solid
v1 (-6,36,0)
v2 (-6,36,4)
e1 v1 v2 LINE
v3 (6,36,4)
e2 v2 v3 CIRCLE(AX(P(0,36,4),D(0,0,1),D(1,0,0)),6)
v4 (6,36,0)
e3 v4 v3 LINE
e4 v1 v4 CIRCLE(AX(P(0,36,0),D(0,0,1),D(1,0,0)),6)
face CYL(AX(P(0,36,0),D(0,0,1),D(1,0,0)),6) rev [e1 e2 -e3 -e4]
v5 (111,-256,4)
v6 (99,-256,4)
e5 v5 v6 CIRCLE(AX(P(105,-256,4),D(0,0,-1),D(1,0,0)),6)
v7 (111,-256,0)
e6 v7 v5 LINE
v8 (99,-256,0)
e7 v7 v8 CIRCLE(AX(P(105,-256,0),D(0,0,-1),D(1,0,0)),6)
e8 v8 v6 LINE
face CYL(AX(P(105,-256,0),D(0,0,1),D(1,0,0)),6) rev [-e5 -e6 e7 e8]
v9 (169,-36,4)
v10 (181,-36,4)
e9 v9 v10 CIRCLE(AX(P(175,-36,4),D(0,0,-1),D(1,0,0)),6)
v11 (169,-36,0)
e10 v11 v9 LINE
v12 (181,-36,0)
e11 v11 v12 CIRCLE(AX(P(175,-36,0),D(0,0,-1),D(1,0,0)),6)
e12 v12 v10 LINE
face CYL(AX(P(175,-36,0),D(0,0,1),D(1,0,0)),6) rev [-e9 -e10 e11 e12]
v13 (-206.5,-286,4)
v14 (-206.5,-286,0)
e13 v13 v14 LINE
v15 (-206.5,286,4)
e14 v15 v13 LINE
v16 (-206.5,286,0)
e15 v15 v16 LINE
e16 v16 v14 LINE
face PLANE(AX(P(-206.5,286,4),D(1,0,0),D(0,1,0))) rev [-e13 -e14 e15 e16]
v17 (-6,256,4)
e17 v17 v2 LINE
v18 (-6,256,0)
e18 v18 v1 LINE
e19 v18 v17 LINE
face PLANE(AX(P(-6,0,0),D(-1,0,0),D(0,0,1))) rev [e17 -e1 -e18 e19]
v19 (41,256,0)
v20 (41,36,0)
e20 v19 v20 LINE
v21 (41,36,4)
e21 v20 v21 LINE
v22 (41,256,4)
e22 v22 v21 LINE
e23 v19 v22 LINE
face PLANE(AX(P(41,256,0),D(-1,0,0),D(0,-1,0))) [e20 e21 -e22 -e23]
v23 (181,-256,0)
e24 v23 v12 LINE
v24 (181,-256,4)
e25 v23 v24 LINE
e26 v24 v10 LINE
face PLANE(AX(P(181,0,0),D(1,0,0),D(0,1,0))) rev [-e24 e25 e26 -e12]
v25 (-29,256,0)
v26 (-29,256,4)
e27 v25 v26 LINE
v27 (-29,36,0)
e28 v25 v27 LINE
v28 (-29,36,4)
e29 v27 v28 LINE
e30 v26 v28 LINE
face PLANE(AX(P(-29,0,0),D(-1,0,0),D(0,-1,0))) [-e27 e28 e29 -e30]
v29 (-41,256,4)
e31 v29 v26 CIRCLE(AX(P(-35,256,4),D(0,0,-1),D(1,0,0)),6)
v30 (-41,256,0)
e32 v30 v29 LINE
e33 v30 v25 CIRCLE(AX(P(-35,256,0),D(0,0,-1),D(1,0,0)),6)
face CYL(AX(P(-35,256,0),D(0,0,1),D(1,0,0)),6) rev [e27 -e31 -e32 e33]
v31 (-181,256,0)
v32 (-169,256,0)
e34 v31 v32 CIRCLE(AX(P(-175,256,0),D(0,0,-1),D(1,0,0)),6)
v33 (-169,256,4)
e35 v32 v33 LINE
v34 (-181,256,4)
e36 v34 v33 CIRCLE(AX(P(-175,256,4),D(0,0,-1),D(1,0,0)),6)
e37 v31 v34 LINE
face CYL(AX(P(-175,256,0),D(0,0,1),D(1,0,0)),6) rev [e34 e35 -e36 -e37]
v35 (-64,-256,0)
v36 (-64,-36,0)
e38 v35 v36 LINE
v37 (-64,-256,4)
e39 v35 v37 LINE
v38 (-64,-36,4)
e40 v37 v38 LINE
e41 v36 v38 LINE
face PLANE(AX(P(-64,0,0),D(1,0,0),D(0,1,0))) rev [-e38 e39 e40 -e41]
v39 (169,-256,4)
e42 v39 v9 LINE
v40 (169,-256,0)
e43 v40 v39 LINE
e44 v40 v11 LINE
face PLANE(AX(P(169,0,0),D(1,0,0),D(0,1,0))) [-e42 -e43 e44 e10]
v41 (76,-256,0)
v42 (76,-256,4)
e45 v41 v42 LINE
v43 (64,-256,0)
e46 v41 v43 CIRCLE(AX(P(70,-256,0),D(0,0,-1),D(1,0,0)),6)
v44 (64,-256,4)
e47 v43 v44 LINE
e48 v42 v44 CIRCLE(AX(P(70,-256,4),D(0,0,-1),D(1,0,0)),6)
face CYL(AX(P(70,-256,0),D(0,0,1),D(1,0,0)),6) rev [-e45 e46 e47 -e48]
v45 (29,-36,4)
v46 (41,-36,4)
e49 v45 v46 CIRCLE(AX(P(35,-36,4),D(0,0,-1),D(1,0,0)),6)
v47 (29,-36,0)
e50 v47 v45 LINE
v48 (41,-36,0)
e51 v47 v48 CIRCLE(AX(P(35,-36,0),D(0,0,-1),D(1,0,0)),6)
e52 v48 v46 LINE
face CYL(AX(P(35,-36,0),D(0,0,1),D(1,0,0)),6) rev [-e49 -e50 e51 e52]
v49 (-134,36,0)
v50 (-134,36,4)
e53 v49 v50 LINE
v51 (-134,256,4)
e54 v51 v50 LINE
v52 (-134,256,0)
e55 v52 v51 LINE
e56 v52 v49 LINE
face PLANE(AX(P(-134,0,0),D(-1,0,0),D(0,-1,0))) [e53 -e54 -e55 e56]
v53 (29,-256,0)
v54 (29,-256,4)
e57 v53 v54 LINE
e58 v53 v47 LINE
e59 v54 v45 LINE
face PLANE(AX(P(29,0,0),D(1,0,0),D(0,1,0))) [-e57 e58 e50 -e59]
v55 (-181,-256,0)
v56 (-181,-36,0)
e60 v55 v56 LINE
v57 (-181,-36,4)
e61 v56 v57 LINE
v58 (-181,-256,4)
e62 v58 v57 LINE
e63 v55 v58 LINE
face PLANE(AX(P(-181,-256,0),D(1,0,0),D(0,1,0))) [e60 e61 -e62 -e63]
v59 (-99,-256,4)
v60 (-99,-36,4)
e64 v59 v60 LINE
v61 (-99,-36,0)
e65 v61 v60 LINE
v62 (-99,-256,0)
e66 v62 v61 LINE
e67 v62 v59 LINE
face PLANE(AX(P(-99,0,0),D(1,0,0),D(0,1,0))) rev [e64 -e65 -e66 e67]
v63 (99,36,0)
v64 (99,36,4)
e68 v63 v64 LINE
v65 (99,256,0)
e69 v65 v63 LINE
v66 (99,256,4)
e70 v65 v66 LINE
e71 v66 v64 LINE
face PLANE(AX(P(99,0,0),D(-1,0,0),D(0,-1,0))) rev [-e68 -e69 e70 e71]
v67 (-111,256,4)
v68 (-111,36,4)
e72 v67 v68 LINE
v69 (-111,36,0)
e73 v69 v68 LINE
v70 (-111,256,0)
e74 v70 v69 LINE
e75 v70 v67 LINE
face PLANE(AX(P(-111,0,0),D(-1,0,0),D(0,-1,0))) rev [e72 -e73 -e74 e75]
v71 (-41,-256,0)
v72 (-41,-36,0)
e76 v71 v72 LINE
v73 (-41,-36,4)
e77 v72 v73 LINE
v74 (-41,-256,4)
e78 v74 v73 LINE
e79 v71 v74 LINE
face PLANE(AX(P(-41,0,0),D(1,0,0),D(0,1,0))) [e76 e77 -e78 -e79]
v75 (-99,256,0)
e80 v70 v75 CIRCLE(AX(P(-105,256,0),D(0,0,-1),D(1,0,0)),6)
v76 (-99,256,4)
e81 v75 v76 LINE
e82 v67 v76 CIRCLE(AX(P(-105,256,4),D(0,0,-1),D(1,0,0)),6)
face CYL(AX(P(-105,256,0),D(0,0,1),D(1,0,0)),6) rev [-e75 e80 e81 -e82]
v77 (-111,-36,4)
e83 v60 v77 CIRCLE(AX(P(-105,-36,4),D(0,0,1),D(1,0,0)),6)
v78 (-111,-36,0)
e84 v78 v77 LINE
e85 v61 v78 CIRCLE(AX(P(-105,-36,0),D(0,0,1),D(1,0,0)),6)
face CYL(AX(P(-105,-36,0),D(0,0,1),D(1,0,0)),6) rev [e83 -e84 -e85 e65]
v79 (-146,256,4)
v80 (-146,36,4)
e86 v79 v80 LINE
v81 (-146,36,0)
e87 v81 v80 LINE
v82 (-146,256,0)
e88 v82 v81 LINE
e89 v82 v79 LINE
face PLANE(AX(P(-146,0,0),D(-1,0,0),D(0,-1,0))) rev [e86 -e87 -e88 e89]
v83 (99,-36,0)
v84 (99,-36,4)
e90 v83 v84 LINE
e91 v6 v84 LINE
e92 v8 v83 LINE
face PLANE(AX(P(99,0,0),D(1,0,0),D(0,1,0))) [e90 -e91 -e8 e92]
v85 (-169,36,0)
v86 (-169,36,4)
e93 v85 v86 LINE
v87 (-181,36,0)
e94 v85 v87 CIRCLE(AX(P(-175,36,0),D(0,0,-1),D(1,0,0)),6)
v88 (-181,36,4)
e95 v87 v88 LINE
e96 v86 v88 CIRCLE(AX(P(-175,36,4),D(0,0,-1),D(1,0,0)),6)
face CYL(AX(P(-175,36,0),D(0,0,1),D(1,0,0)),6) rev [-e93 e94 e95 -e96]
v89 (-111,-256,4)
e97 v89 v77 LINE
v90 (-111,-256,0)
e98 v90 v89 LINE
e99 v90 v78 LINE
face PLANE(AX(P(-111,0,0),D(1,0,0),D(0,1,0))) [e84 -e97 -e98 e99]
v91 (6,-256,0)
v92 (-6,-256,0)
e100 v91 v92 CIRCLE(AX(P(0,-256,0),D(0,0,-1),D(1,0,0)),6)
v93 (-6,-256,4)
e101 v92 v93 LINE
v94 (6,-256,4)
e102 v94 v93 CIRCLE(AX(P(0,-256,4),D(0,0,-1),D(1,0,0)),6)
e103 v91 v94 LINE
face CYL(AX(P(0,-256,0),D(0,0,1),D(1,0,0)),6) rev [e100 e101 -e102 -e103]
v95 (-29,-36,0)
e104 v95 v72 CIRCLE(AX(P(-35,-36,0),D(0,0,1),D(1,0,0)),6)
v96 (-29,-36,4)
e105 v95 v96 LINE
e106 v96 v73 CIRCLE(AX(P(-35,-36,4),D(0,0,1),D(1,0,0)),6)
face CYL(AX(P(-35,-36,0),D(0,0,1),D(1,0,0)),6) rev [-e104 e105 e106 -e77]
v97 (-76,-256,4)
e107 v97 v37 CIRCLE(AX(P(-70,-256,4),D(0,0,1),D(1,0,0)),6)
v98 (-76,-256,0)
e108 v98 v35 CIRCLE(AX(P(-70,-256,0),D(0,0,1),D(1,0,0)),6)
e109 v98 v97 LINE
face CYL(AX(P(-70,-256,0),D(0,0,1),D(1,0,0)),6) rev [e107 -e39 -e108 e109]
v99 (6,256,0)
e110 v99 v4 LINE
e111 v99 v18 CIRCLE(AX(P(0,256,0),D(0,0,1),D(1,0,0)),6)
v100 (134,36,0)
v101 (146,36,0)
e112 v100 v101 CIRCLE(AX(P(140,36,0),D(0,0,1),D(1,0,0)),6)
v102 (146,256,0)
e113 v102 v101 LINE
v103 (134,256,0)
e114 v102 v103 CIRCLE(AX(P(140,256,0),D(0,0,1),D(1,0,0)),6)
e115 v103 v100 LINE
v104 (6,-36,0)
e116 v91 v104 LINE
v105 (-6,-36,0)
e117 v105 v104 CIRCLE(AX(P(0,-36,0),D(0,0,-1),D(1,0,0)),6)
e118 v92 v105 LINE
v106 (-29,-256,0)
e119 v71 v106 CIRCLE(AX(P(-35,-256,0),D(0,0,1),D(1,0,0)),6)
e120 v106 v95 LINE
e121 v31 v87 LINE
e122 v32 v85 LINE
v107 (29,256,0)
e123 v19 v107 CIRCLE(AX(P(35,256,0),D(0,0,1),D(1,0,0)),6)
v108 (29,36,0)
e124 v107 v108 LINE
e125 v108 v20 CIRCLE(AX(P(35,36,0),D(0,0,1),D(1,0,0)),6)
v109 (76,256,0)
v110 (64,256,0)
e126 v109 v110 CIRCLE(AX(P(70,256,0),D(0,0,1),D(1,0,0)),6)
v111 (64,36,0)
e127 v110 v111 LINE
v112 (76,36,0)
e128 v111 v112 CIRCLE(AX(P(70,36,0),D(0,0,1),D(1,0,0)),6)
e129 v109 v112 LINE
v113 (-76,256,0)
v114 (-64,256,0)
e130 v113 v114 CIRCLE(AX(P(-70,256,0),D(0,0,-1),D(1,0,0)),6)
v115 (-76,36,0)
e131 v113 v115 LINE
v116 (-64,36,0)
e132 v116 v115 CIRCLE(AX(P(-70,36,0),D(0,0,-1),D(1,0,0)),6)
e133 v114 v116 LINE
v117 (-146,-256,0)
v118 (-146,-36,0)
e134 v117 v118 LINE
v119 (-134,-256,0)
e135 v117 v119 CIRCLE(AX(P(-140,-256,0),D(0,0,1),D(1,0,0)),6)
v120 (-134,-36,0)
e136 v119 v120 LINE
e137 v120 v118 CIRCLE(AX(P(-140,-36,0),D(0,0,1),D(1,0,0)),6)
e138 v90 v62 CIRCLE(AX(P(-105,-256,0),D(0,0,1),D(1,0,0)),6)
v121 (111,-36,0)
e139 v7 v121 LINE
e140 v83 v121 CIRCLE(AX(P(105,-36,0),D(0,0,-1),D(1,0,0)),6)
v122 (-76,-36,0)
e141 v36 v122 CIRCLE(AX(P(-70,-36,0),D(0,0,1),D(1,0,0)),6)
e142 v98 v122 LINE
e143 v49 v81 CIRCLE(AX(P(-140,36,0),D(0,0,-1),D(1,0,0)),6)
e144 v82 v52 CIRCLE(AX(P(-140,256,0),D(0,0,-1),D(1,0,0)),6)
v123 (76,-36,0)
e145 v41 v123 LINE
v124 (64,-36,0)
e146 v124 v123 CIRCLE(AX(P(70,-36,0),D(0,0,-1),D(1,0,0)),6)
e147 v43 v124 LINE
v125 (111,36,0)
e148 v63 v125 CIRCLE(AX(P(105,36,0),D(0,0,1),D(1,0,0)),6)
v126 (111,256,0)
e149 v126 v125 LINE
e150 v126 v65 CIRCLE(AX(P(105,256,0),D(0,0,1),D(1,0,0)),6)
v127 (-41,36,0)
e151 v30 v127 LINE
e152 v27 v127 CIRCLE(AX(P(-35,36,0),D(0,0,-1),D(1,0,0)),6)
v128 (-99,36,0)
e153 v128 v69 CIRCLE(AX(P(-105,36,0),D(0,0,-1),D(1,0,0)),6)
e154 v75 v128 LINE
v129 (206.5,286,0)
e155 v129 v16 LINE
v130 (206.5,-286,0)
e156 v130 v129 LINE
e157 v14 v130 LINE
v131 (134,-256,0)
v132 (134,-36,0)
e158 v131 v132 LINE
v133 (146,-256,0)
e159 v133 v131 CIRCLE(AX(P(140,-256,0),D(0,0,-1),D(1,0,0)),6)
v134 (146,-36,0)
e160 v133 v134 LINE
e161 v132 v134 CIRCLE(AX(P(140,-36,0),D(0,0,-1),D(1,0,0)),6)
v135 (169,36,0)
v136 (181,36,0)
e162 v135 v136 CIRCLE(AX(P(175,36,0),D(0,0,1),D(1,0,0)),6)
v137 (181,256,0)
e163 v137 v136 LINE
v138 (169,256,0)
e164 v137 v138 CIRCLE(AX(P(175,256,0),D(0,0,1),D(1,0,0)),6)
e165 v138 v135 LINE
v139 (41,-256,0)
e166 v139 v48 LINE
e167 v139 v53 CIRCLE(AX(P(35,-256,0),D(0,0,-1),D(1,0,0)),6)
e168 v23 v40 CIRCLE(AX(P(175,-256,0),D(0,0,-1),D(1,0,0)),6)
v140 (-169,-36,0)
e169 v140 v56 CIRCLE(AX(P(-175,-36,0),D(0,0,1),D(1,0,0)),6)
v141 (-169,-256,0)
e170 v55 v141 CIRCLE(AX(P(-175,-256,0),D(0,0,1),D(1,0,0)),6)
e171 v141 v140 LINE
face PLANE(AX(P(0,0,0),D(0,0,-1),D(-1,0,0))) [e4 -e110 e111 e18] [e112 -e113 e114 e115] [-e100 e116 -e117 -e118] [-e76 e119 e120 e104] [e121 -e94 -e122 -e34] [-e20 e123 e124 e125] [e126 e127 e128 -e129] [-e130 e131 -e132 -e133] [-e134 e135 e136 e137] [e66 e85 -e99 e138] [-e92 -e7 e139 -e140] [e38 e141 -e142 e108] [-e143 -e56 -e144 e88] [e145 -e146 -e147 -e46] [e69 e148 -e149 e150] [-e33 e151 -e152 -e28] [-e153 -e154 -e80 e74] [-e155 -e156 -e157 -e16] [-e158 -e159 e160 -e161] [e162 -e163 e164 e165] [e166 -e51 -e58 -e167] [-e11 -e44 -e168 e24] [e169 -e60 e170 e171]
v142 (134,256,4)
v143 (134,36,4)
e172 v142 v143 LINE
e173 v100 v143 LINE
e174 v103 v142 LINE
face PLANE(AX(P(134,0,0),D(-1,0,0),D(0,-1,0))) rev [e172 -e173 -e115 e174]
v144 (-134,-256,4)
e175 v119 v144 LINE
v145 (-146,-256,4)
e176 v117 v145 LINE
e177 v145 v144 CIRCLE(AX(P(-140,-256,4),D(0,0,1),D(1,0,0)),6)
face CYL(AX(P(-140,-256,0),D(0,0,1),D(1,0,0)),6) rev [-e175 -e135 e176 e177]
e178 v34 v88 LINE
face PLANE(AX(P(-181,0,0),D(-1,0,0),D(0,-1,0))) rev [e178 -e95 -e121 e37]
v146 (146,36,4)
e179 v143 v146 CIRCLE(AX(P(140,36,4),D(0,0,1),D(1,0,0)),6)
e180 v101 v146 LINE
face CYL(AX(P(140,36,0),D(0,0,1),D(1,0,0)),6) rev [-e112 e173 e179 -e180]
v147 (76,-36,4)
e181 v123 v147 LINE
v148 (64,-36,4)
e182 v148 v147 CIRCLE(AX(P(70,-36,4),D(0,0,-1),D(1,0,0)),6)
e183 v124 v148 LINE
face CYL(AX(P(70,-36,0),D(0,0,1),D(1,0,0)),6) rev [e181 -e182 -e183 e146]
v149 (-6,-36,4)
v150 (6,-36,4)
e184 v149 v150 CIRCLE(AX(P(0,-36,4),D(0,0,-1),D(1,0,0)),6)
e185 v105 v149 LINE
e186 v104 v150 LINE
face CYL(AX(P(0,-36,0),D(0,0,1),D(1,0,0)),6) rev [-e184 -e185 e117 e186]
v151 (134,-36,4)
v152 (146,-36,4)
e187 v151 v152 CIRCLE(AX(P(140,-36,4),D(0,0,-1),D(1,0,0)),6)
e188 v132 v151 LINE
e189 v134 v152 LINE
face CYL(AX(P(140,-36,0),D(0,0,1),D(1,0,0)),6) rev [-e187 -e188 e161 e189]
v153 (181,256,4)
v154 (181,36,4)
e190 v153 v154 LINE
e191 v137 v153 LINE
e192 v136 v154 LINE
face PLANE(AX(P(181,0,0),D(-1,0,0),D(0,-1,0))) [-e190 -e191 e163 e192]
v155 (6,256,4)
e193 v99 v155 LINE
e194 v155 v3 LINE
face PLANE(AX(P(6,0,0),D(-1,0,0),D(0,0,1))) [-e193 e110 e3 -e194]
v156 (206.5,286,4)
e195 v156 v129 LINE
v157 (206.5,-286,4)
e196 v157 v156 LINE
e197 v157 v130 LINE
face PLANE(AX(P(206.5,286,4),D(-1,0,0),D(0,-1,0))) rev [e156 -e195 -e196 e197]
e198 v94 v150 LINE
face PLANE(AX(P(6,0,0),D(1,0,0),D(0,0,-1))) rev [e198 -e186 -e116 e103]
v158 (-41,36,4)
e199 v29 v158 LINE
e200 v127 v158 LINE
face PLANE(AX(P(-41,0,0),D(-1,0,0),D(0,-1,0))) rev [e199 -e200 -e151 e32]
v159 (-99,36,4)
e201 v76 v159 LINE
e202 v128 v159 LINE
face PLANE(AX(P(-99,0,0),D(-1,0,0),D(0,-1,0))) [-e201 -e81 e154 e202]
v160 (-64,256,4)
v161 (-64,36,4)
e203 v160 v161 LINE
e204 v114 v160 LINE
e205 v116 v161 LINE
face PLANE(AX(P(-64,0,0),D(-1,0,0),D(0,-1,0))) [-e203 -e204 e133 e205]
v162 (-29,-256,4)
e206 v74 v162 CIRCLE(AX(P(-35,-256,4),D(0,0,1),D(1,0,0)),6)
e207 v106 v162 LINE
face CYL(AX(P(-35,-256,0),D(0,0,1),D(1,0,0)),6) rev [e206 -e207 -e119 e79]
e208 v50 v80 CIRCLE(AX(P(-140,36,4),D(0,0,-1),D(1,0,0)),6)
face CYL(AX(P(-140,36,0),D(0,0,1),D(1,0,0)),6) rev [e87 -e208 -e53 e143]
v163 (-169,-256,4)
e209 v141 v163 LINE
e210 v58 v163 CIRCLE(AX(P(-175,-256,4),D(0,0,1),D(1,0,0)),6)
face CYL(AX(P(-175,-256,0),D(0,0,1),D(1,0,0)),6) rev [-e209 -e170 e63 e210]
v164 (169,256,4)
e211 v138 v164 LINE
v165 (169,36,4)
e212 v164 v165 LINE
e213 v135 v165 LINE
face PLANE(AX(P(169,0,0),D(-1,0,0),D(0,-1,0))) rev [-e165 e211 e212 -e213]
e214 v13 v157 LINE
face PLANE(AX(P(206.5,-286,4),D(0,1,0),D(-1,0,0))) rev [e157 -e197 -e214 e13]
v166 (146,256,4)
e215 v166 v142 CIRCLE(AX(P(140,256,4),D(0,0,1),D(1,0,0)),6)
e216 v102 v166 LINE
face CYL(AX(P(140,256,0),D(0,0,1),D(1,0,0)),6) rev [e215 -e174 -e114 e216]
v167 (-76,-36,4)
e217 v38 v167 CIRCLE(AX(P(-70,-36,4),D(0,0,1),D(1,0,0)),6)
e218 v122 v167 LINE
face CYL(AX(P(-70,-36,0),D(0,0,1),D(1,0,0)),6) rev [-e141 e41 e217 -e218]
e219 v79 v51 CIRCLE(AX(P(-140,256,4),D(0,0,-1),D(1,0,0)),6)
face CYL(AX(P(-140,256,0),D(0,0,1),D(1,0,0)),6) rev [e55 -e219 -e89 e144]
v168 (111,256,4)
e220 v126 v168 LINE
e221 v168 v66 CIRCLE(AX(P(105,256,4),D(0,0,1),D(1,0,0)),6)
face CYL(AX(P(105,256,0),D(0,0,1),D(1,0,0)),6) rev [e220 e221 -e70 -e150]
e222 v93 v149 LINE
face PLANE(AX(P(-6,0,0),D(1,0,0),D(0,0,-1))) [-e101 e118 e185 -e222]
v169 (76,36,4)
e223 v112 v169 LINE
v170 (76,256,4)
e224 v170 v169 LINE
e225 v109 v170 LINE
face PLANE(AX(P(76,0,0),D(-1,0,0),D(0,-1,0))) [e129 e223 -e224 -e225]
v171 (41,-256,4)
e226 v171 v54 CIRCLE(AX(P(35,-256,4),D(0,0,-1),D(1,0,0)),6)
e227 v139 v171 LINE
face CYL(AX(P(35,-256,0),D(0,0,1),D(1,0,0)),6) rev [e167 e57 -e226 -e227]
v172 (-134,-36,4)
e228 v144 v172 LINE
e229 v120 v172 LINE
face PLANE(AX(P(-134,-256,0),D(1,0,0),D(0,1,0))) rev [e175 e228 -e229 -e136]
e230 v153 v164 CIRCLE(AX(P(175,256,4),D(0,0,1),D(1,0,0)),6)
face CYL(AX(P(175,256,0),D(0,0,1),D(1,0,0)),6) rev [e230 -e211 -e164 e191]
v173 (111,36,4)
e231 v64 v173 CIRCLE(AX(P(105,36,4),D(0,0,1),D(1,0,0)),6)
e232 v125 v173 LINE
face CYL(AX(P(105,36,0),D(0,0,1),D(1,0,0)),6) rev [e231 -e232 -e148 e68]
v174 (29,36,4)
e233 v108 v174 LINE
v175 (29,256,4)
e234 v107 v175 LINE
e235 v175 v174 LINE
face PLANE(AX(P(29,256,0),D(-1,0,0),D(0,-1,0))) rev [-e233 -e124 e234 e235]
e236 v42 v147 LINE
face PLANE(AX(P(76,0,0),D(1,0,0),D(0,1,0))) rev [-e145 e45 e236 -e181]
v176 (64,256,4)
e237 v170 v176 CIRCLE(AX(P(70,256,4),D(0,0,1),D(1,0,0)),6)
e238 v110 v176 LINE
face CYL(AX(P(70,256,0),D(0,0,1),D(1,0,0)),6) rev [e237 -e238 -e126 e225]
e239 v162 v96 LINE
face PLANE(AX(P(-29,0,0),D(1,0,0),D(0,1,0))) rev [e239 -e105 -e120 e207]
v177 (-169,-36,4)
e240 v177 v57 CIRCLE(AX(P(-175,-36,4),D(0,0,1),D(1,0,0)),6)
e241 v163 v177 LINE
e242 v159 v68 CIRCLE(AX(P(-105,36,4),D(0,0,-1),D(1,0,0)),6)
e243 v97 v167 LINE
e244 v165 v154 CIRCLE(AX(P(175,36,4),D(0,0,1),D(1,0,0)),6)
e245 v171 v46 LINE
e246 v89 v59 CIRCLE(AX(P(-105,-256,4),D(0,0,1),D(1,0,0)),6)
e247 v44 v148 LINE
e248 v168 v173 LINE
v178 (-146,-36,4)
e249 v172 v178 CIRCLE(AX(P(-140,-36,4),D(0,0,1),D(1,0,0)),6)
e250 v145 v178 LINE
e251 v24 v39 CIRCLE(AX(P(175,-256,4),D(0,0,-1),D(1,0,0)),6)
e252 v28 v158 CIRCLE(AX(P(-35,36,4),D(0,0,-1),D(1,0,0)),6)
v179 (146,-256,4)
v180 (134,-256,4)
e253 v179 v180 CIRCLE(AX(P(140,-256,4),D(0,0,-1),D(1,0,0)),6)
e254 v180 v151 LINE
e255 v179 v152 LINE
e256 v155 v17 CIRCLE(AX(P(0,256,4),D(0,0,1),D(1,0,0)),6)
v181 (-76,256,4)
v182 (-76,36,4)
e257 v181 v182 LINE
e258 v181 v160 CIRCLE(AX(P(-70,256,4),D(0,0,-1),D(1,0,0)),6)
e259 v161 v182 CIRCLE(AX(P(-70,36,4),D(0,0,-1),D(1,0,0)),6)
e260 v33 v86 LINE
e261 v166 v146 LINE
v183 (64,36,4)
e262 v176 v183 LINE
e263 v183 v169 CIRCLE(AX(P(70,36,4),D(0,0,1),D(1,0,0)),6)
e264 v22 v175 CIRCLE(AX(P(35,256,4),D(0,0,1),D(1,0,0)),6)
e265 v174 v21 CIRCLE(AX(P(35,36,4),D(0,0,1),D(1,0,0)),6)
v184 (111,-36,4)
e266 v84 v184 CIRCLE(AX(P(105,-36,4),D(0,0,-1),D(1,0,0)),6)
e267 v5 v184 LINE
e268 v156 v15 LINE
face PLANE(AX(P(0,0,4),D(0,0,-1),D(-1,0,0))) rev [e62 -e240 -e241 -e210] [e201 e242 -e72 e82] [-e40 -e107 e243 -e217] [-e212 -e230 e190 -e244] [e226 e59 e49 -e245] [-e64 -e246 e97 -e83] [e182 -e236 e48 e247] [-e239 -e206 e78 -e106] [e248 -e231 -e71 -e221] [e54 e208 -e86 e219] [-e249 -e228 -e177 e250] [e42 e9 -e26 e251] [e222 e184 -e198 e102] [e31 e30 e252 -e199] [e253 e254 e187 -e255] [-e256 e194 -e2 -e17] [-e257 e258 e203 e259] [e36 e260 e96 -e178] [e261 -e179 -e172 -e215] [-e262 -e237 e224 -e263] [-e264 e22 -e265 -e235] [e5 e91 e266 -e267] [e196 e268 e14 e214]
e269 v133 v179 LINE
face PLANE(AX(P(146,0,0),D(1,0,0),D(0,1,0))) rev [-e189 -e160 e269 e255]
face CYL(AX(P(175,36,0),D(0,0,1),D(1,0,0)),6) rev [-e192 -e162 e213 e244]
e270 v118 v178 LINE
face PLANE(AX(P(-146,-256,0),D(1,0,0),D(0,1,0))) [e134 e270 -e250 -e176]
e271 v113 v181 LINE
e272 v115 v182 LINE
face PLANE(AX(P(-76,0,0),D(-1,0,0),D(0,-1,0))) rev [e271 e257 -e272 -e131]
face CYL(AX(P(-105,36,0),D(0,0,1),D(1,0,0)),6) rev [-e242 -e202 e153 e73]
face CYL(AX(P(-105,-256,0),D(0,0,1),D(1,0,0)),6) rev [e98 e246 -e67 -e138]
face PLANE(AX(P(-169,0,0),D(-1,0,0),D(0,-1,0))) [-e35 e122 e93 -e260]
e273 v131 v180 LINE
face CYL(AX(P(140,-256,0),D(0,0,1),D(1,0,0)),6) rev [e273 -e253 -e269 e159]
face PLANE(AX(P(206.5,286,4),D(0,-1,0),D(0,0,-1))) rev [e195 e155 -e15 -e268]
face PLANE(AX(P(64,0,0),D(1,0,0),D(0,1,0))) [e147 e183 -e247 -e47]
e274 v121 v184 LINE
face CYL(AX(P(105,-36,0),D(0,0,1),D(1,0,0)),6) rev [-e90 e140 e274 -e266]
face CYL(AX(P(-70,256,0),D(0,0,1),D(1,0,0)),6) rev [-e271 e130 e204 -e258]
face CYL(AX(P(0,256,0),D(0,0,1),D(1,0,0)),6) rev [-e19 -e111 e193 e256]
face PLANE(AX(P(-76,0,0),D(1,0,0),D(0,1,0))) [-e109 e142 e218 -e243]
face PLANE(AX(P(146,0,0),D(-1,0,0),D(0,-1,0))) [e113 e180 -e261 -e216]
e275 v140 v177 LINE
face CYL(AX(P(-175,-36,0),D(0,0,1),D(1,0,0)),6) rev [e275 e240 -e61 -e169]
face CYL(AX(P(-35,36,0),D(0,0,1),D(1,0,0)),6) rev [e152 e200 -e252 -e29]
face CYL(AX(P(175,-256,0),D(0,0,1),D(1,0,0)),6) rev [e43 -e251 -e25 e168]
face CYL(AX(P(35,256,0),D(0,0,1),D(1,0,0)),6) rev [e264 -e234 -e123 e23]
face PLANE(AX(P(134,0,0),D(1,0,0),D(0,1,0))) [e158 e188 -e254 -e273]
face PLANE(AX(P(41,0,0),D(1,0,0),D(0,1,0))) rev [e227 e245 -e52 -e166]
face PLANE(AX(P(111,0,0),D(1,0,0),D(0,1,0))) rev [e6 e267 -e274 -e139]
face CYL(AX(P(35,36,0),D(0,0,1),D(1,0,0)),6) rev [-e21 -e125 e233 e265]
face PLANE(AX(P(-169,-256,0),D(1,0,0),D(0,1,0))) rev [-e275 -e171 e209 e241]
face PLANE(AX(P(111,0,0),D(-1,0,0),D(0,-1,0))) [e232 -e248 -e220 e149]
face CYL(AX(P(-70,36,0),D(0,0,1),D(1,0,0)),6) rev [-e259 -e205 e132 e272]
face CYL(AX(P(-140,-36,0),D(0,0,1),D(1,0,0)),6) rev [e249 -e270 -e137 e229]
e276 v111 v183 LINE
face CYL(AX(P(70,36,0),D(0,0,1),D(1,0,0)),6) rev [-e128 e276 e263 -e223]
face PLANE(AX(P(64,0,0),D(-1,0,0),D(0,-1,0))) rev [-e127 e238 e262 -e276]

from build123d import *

# Parameters (mm, degrees)
SKETCH1_W           = 413
SKETCH1_H           = 572
BOSS_EXTRUDE1_DEPTH = 4
CUT_EXTRUDE1_DEPTH  = 4


with BuildPart() as part:
    # Sketch1 → Boss-Extrude1 (new body)
    with BuildSketch(Plane.XY):
        Rectangle(SKETCH1_W, SKETCH1_H)
    extrude(amount=BOSS_EXTRUDE1_DEPTH)

    # Sketch2 → Cut-Extrude1 (cut)
    with BuildSketch(Plane.XY.offset(4)):
        with BuildLine():
            Line((-99, -256), (-99, -36))
            ThreePointArc((-99, -36), (-105, -30), (-111, -36))
            Line((-111, -36), (-111, -256))
            ThreePointArc((-111, -256), (-105, -262), (-99, -256))
        make_face()
        with BuildLine():
            Line((-64, -256), (-64, -36))
            ThreePointArc((-64, -36), (-70, -30), (-76, -36))
            Line((-76, -36), (-76, -256))
            ThreePointArc((-76, -256), (-70, -262), (-64, -256))
        make_face()
        with BuildLine():
            Line((-29, -256), (-29, -36))
            ThreePointArc((-29, -36), (-35, -30), (-41, -36))
            Line((-41, -36), (-41, -256))
            ThreePointArc((-41, -256), (-35, -262), (-29, -256))
        make_face()
        with BuildLine():
            ThreePointArc((-6, -36), (0, -30), (6, -36))
            Line((6, -36), (6, -256))
            ThreePointArc((6, -256), (0, -262), (-6, -256))
            Line((-6, -256), (-6, -36))
        make_face()
        with BuildLine():
            ThreePointArc((29, -36), (35, -30), (41, -36))
            Line((41, -36), (41, -256))
            ThreePointArc((41, -256), (35, -262), (29, -256))
            Line((29, -256), (29, -36))
        make_face()
        with BuildLine():
            ThreePointArc((64, -36), (70, -30), (76, -36))
            Line((76, -36), (76, -256))
            ThreePointArc((76, -256), (70, -262), (64, -256))
            Line((64, -256), (64, -36))
        make_face()
        with BuildLine():
            ThreePointArc((169, -36), (175, -30), (181, -36))
            Line((181, -36), (181, -256))
            ThreePointArc((181, -256), (175, -262), (169, -256))
            Line((169, -256), (169, -36))
        make_face()
        with BuildLine():
            ThreePointArc((134, -36), (140, -30), (146, -36))
            Line((146, -36), (146, -256))
            ThreePointArc((146, -256), (140, -262), (134, -256))
            Line((134, -256), (134, -36))
        make_face()
        with BuildLine():
            ThreePointArc((99, -36), (105, -30), (111, -36))
            Line((111, -36), (111, -256))
            ThreePointArc((111, -256), (105, -262), (99, -256))
            Line((99, -256), (99, -36))
        make_face()
        with BuildLine():
            ThreePointArc((-169, 36), (-175, 30), (-181, 36))
            Line((-181, 36), (-181, 256))
            ThreePointArc((-181, 256), (-175, 262), (-169, 256))
            Line((-169, 256), (-169, 36))
        make_face()
        with BuildLine():
            ThreePointArc((-134, 36), (-140, 30), (-146, 36))
            Line((-146, 36), (-146, 256))
            ThreePointArc((-146, 256), (-140, 262), (-134, 256))
            Line((-134, 256), (-134, 36))
        make_face()
        with BuildLine():
            ThreePointArc((-99, 36), (-105, 30), (-111, 36))
            Line((-111, 36), (-111, 256))
            ThreePointArc((-111, 256), (-105, 262), (-99, 256))
            Line((-99, 256), (-99, 36))
        make_face()
        with BuildLine():
            ThreePointArc((-64, 36), (-70, 30), (-76, 36))
            Line((-76, 36), (-76, 256))
            ThreePointArc((-76, 256), (-70, 262), (-64, 256))
            Line((-64, 256), (-64, 36))
        make_face()
        with BuildLine():
            ThreePointArc((-29, 36), (-35, 30), (-41, 36))
            Line((-41, 36), (-41, 256))
            ThreePointArc((-41, 256), (-35, 262), (-29, 256))
            Line((-29, 256), (-29, 36))
        make_face()
        with BuildLine():
            Line((-6, 256), (-6, 36))
            ThreePointArc((-6, 36), (0, 30), (6, 36))
            Line((6, 36), (6, 256))
            ThreePointArc((6, 256), (0, 262), (-6, 256))
        make_face()
        with BuildLine():
            Line((64, 256), (64, 36))
            ThreePointArc((64, 36), (70, 30), (76, 36))
            Line((76, 36), (76, 256))
            ThreePointArc((76, 256), (70, 262), (64, 256))
        make_face()
        with BuildLine():
            Line((99, 256), (99, 36))
            ThreePointArc((99, 36), (105, 30), (111, 36))
            Line((111, 36), (111, 256))
            ThreePointArc((111, 256), (105, 262), (99, 256))
        make_face()
        with BuildLine():
            Line((134, 256), (134, 36))
            ThreePointArc((134, 36), (140, 30), (146, 36))
            Line((146, 36), (146, 256))
            ThreePointArc((146, 256), (140, 262), (134, 256))
        make_face()
        with BuildLine():
            Line((169, 256), (169, 36))
            ThreePointArc((169, 36), (175, 30), (181, 36))
            Line((181, 36), (181, 256))
            ThreePointArc((181, 256), (175, 262), (169, 256))
        make_face()
        with BuildLine():
            Line((-181, -256), (-181, -36))
            ThreePointArc((-181, -36), (-175, -30), (-169, -36))
            Line((-169, -36), (-169, -256))
            ThreePointArc((-169, -256), (-175, -262), (-181, -256))
        make_face()
        with BuildLine():
            Line((-146, -256), (-146, -36))
            ThreePointArc((-146, -36), (-140, -30), (-134, -36))
            Line((-134, -36), (-134, -256))
            ThreePointArc((-134, -256), (-140, -262), (-146, -256))
        make_face()
        with BuildLine():
            Line((29, 256), (29, 36))
            ThreePointArc((29, 36), (35, 30), (41, 36))
            Line((41, 36), (41, 256))
            ThreePointArc((41, 256), (35, 262), (29, 256))
        make_face()
    extrude(amount=-CUT_EXTRUDE1_DEPTH, mode=Mode.SUBTRACT)


solid = part.part
